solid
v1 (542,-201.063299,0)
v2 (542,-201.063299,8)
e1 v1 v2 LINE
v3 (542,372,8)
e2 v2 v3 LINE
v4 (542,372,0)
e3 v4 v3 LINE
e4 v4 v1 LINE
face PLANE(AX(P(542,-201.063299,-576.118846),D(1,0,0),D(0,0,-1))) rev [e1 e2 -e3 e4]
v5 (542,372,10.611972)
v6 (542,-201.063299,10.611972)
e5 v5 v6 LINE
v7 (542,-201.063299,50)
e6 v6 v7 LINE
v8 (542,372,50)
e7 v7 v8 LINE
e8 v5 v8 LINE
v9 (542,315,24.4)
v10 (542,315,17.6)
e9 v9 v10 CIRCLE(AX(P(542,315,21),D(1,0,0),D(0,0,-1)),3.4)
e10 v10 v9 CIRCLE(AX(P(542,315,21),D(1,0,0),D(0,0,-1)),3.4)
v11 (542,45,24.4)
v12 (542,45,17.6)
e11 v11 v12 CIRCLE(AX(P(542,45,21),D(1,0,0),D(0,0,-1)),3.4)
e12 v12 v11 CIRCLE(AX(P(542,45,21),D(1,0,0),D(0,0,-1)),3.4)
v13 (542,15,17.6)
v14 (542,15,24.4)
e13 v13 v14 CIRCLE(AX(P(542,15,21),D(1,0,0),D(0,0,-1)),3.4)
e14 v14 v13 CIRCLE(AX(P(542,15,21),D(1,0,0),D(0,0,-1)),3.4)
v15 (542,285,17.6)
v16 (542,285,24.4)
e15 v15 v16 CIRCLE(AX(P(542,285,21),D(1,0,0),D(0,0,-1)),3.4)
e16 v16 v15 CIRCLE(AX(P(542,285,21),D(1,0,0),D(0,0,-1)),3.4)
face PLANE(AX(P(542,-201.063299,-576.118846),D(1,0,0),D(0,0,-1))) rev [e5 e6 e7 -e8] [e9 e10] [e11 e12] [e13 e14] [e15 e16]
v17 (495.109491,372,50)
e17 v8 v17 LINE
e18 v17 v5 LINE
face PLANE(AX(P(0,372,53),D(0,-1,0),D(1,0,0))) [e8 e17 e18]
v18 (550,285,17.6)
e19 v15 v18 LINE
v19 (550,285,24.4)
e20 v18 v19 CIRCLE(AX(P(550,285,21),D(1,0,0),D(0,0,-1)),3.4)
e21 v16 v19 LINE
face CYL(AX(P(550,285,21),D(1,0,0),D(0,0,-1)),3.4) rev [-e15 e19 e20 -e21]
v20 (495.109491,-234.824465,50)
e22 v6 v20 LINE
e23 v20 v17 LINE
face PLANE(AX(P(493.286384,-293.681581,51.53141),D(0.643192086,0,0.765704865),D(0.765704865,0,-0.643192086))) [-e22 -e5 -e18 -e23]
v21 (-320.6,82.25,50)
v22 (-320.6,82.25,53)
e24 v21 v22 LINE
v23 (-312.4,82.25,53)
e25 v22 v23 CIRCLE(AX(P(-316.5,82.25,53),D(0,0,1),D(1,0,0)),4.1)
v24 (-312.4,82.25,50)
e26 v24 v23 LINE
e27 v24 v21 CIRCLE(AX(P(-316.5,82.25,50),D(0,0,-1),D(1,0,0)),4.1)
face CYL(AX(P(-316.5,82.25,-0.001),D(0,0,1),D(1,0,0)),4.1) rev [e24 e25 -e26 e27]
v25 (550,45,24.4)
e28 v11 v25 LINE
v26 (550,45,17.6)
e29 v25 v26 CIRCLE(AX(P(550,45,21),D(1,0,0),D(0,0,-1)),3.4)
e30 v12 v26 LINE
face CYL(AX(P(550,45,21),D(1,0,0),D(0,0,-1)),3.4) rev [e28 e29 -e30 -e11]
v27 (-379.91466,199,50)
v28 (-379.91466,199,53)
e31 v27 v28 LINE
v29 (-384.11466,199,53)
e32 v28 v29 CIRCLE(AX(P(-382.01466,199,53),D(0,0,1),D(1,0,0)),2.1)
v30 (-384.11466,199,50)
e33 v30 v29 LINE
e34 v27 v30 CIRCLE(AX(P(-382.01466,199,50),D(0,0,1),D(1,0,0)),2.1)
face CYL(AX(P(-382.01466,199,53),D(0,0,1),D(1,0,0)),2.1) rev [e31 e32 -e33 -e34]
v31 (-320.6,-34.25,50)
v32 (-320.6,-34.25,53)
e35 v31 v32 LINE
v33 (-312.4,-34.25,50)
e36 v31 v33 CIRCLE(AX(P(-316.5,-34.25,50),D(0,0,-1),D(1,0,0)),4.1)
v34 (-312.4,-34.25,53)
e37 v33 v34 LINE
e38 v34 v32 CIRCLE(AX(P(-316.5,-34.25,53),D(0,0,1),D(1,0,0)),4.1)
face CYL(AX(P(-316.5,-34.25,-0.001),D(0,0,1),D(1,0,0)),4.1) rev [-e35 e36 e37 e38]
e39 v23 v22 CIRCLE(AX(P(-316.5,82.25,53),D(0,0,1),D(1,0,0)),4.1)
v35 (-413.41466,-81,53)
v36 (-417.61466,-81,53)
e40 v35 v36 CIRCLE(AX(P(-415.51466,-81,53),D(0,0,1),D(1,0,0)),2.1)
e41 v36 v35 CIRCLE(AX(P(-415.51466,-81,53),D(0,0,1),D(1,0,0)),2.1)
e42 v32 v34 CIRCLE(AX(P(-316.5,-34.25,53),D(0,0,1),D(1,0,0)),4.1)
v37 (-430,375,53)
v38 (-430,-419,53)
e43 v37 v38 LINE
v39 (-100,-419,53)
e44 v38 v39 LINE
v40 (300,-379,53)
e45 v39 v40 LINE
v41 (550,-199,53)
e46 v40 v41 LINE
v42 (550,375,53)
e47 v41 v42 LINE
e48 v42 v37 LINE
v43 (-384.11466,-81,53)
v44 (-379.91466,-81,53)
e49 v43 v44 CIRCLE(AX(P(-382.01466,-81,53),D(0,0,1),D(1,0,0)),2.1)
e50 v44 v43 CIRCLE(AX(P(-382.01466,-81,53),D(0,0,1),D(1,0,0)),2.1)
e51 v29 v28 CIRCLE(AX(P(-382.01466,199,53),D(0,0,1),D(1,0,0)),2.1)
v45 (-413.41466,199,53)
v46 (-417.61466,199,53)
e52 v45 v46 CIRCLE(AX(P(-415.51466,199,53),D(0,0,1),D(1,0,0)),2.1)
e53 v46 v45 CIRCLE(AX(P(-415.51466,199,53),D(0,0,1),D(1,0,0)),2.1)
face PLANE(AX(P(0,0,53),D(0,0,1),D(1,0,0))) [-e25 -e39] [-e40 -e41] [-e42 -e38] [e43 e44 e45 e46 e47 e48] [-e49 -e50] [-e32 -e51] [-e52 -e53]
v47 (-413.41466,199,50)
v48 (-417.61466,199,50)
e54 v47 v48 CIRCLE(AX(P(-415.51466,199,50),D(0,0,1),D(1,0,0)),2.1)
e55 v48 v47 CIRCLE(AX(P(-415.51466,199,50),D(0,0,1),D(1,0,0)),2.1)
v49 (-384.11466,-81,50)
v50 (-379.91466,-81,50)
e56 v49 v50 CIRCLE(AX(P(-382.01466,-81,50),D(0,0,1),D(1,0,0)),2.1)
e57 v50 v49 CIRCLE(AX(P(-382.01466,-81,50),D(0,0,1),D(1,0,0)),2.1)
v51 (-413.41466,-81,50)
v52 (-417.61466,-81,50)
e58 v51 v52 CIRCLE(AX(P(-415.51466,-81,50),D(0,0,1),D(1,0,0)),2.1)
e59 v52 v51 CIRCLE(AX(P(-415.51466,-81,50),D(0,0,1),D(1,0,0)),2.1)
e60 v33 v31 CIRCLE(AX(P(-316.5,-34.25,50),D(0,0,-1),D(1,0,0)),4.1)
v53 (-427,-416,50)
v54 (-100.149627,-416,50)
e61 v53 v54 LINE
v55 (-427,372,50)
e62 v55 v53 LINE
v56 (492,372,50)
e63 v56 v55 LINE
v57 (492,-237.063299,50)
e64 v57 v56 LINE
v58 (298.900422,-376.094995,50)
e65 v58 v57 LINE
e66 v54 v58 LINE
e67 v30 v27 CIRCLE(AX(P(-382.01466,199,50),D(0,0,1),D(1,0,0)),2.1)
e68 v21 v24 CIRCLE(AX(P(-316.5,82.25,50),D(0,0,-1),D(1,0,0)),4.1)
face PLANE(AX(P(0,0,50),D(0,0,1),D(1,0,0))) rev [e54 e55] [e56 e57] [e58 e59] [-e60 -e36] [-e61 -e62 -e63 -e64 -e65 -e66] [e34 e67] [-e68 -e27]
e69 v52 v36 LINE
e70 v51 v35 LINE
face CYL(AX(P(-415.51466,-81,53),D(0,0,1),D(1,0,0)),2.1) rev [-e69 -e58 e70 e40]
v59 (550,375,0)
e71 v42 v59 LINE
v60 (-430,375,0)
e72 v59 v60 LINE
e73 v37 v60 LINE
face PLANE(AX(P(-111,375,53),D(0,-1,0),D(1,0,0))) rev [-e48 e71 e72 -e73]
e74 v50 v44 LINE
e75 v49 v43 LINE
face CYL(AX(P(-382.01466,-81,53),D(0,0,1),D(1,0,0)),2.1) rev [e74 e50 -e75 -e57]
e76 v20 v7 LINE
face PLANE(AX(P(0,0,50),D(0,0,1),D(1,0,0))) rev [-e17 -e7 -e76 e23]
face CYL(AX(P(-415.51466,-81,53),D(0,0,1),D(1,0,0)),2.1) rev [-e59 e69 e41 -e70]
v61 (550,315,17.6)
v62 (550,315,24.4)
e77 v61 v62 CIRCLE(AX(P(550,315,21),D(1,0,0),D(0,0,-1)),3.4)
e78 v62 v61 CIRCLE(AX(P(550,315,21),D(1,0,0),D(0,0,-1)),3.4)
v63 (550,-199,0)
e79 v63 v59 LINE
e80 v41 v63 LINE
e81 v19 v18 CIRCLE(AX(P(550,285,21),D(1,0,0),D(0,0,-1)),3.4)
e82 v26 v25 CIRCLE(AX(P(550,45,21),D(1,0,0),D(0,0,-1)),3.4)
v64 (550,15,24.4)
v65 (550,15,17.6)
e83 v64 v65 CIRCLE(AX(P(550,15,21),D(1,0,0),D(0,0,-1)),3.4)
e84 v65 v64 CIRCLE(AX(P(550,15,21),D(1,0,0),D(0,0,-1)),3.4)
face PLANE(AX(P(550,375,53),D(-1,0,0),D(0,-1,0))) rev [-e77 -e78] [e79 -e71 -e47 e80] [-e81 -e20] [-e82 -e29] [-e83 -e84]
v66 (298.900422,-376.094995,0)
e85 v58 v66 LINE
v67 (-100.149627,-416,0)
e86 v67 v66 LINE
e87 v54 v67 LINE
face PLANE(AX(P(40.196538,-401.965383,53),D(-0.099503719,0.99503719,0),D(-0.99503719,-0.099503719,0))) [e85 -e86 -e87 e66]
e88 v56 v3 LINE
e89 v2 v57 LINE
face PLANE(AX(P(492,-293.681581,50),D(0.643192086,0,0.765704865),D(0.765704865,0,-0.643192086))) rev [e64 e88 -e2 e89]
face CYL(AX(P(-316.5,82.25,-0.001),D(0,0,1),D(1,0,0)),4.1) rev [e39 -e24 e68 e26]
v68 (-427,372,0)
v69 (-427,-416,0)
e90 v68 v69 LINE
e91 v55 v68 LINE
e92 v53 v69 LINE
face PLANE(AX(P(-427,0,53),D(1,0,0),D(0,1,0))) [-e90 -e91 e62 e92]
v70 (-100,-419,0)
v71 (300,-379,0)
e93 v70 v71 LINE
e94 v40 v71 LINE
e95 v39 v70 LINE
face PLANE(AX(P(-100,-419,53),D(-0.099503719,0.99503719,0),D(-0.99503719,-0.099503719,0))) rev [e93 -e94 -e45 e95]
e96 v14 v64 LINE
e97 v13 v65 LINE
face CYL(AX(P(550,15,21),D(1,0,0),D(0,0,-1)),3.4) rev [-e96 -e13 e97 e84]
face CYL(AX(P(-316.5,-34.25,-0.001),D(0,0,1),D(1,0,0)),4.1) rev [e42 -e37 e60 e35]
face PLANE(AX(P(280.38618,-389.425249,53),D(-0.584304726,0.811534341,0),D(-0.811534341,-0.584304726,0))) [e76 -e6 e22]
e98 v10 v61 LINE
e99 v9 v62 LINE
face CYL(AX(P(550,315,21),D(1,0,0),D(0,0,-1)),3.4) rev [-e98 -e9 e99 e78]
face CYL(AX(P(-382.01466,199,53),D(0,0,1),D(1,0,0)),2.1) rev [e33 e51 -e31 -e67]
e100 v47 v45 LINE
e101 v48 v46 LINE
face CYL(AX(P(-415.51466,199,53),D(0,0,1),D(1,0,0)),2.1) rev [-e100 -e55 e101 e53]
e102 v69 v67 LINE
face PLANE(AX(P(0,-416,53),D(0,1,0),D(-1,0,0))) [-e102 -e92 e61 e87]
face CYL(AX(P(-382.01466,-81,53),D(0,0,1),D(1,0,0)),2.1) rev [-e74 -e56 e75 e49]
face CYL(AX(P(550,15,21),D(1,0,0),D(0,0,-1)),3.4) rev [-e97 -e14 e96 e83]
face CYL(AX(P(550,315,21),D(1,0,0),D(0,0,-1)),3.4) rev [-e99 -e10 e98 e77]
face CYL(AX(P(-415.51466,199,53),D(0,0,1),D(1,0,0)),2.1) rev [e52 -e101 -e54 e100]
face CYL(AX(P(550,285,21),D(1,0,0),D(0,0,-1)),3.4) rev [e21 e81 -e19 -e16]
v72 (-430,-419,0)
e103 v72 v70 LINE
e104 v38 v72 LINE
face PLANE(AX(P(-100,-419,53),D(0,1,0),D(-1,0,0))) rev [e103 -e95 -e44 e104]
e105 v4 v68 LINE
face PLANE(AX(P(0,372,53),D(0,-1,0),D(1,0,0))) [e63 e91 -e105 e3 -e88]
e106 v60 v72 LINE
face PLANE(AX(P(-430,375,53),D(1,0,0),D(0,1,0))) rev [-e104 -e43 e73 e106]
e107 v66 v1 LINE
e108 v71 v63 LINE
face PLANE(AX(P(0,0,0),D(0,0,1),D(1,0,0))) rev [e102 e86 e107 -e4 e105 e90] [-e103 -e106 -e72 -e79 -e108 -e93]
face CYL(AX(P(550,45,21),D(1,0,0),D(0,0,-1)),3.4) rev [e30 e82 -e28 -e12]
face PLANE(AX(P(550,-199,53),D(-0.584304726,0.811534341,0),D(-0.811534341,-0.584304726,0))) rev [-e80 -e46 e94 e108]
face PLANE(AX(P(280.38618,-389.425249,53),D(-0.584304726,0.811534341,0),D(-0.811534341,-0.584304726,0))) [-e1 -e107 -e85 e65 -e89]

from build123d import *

# Parameters (mm, degrees)
EXTRUDE_1_DEPTH        = 53
EXTRUDE_1_2_DEPTH      = 3
EXTRUDE_2_DEPTH        = 50
EXTRUDE_3_REACH        = 966.878
CUT_EXTRUDE_1_REACH    = 695.448
SKETCH_5_R             = 4.1
HOLE_WIZARD_M8_1_D     = 6.8
HOLE_WIZARD_M8_1_DEPTH = 8
HOLE_WIZARD_M5_1_D     = 4.2
HOLE_WIZARD_M5_1_DEPTH = 14
HOLE_WIZARD_M5_1_TIP   = 1.2618073


with BuildPart() as part:
    # 草图1 → Extrude 1 (new body)
    with BuildSketch(Plane.XY):
        Polygon((-430, 375), (-111, 375), (550, 375), (550, -199), (300, -379), (-100, -419), (-430, -419), align=None)
        Polygon((-427, 372), (-111, 372), (547, 372), (547, -197.463298768), (298.9004217, -376.094995144), (-100.149626863, -416), (-427, -416), align=None, mode=Mode.SUBTRACT)
    extrude(amount=EXTRUDE_1_DEPTH)

    # 草图2 → Extrude 1 2 (add)
    with BuildSketch(Plane(origin=(0, 0, 53), x_dir=(-1, 0, 0), z_dir=(0, 0, -1))):
        Polygon((100, -419), (430, -419), (430, 375), (-550, 375), (-550, -199), (-300, -379), align=None)
    extrude(amount=EXTRUDE_1_2_DEPTH)

    # 草图3 → 凸台-拉伸2 (add)
    with BuildSketch(Plane(origin=(0, 0, 50), x_dir=(-1, 0, 0), z_dir=(0, 0, -1))):
        Polygon((-542, 375), (-550, 375), (-550, -199), (-544.865692733, -199), (-542, -201.063298768), (-542, -199.063298768), align=None)
    extrude(amount=EXTRUDE_2_DEPTH)

    # 拉伸-薄壁3: up to this plane
    extrude_3_end = Plane(origin=(280.386179605, -389.425249452, 53), z_dir=(-0.584304725845076, 0.8115343414514945, 0))
    # 草图4 → 拉伸-薄壁3 (add, up to the surface)
    with BuildSketch(Plane.XZ.offset(-372), mode=Mode.PRIVATE) as extrude_3_sk1:
        Polygon((492, 50), (542, 8), (543.286384173, 9.53140973), (493.286384173, 51.53140973), align=None)
    extrude_3_tool1 = split(extrude(extrude_3_sk1.sketch, amount=EXTRUDE_3_REACH, mode=Mode.PRIVATE), bisect_by=extrude_3_end, keep=Keep.BOTH, mode=Mode.PRIVATE)
    add(extrude_3_tool1.solids().sort_by_distance((517.643192, 372, 29.765705))[0])

    # 草图5 → 切除-拉伸1 (cut, up to next)
    with BuildSketch(Plane.XY.offset(53), mode=Mode.PRIVATE) as cut_extrude_1_sk1:
        with Locations((-316.5, 82.25)):
            Circle(SKETCH_5_R)
    cut_extrude_1_tool1 = extrude(cut_extrude_1_sk1.sketch, amount=-CUT_EXTRUDE_1_REACH, mode=Mode.PRIVATE) & part.part
    # 草图5 → 切除-拉伸1 (cut, up to next)
    with BuildSketch(Plane.XY.offset(53), mode=Mode.PRIVATE) as cut_extrude_1_sk2:
        with Locations((-316.5, -34.25)):
            Circle(SKETCH_5_R)
    cut_extrude_1_tool2 = extrude(cut_extrude_1_sk2.sketch, amount=-CUT_EXTRUDE_1_REACH, mode=Mode.PRIVATE) & part.part
    add(cut_extrude_1_tool1.solids().sort_by_distance((-316.5, 82.25, 53))[0], mode=Mode.SUBTRACT)
    add(cut_extrude_1_tool2.solids().sort_by_distance((-316.5, -34.25, 53))[0], mode=Mode.SUBTRACT)

    # M8 螺纹孔1
    with Locations(Plane(origin=(550, 0, 0), x_dir=(0, 0, -1), z_dir=(1, 0, 0))):
        with Locations((-21, 315), (-21, 285), (-21, 45), (-21, 15)):
            Hole(HOLE_WIZARD_M8_1_D / 2, depth=HOLE_WIZARD_M8_1_DEPTH)

    # M5 螺纹孔1
    with Locations(Plane.XY.offset(53)):
        with Locations((-415.514659804, 199), (-382.014659804, 199), (-415.514659804, -81), (-382.014659804, -81)):
            Hole(HOLE_WIZARD_M5_1_D / 2, depth=HOLE_WIZARD_M5_1_DEPTH)
            with Locations((0, 0, -(HOLE_WIZARD_M5_1_DEPTH + HOLE_WIZARD_M5_1_TIP / 2))):  # 118° drill point
                Cone(0, HOLE_WIZARD_M5_1_D / 2, HOLE_WIZARD_M5_1_TIP, mode=Mode.SUBTRACT)


solid = part.part
